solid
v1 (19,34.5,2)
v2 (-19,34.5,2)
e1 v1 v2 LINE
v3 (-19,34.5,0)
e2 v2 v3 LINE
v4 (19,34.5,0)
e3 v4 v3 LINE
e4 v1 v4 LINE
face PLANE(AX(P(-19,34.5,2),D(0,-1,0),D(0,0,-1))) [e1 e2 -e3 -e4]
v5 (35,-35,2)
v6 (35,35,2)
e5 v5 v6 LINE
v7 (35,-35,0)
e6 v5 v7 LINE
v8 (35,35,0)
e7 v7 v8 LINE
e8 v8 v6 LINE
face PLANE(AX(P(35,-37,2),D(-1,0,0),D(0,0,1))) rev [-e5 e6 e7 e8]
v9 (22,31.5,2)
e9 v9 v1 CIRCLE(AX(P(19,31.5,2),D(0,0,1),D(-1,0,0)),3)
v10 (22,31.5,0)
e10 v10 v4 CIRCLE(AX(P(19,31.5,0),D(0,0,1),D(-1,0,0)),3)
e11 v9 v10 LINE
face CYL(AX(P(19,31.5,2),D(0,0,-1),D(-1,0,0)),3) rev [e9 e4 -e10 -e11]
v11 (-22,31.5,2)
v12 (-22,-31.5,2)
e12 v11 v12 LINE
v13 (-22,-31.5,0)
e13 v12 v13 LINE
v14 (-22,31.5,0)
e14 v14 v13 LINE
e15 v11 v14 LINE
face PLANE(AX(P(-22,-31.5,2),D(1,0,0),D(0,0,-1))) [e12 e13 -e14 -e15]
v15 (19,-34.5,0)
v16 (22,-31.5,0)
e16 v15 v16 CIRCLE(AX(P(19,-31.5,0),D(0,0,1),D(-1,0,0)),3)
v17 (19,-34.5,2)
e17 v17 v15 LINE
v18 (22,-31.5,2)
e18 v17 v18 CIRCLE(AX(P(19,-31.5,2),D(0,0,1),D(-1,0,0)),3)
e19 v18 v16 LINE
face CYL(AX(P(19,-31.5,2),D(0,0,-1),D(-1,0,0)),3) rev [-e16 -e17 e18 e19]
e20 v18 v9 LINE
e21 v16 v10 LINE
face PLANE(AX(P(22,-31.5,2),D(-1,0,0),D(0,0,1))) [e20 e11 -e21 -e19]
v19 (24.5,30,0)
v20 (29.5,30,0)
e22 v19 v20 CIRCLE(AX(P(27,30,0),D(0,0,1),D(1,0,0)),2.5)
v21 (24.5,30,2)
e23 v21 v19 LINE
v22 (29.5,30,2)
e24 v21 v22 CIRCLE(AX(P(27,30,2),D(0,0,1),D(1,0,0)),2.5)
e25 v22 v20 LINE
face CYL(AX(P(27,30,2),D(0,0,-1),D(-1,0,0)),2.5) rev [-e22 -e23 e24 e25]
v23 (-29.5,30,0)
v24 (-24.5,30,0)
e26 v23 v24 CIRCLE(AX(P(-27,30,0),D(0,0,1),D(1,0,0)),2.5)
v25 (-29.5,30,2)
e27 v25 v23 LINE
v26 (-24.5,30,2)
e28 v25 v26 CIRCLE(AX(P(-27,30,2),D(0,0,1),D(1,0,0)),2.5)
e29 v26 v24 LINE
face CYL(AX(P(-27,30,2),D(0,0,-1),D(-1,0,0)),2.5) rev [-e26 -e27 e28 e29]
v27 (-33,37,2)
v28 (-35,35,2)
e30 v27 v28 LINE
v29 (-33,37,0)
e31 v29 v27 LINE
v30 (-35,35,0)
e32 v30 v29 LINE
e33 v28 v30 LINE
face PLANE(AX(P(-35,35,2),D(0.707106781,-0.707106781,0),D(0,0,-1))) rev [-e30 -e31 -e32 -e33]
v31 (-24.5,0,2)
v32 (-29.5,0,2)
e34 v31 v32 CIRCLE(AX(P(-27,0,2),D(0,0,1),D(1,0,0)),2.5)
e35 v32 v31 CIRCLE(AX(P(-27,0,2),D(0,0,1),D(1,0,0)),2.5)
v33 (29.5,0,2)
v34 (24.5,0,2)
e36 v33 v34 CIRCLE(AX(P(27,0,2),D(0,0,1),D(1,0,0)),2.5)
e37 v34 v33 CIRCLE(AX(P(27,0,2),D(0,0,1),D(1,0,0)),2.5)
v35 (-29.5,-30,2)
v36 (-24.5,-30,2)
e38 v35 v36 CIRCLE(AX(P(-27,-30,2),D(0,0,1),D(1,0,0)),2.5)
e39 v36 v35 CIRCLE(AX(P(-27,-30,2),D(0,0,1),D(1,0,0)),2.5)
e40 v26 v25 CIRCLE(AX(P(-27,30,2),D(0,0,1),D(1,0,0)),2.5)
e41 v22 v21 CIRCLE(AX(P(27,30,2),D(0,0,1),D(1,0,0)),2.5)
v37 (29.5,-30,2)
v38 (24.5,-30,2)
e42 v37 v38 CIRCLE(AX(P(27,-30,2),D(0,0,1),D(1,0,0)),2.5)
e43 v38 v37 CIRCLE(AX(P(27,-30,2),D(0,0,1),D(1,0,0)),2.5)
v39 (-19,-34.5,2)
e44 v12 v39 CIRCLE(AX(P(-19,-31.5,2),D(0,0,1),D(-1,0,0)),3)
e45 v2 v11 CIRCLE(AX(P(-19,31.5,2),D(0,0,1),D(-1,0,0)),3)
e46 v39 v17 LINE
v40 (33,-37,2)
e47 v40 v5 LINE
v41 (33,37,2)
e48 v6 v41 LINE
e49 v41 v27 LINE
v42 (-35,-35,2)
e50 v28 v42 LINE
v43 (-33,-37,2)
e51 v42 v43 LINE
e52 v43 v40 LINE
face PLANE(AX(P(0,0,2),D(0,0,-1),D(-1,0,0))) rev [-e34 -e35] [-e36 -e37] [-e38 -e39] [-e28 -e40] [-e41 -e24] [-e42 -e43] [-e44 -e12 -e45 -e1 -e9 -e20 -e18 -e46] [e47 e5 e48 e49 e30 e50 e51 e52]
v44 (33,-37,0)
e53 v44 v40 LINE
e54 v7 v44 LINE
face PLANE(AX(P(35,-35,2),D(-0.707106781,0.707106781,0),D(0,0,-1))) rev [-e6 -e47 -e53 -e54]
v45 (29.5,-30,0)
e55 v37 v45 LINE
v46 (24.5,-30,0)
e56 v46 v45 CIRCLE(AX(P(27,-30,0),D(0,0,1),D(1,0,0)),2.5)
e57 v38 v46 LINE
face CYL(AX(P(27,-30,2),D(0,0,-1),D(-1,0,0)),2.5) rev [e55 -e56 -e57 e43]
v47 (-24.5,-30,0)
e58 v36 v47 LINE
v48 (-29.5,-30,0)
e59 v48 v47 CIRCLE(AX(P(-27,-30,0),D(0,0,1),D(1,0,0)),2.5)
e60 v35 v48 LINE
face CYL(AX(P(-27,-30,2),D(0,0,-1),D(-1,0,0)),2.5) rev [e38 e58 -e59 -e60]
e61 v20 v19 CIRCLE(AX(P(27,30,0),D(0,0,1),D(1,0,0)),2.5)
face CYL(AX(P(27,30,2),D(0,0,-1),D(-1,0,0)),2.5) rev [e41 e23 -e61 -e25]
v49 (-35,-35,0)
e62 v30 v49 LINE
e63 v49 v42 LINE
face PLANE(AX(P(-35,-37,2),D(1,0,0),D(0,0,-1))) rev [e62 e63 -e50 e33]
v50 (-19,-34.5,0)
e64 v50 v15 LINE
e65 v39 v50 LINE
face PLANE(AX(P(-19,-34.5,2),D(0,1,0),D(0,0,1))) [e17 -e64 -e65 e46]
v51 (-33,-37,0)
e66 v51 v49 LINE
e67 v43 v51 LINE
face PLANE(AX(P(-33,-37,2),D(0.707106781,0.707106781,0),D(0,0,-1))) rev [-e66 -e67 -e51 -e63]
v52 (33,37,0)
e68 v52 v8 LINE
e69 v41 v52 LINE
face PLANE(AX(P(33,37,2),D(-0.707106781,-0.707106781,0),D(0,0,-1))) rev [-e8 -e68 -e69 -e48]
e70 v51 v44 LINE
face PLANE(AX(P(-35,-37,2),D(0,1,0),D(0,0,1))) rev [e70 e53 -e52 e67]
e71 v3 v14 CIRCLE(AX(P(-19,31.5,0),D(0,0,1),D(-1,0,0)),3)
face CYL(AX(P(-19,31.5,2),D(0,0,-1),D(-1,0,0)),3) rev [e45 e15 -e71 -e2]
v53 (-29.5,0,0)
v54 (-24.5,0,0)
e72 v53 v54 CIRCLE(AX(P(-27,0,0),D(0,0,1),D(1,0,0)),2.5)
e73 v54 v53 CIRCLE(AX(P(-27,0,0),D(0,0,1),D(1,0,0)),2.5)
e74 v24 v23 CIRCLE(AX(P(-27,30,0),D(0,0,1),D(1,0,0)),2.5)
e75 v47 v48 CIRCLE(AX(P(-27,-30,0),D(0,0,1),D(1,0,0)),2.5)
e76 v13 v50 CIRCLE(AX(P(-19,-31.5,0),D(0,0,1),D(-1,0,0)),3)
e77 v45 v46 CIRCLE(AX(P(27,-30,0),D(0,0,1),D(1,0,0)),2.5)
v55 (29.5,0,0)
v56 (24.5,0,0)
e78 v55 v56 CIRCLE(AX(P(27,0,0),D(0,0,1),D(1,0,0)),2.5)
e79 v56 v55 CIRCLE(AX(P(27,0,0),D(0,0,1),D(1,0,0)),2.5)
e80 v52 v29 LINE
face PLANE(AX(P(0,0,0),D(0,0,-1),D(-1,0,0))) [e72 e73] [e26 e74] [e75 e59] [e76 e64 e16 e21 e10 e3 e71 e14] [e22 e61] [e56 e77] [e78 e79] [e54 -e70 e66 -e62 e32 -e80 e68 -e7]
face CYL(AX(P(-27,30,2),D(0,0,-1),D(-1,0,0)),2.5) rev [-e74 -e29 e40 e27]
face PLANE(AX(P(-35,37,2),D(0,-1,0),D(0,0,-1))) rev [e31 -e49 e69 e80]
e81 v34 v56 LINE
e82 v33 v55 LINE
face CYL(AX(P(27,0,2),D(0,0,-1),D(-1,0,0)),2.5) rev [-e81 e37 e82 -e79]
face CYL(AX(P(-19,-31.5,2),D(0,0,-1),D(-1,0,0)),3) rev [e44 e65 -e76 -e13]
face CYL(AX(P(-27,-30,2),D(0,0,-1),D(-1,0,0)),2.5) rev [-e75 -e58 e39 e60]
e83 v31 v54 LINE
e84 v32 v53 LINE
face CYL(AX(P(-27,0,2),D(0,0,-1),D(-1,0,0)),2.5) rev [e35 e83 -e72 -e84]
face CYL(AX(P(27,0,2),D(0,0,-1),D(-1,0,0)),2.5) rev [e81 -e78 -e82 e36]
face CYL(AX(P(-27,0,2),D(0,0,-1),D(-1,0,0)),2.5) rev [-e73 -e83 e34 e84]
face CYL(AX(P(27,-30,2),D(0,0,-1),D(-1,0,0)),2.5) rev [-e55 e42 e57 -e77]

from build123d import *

# Parameters (mm, degrees)
SKETCH1_W           = 70
SKETCH1_H           = 74
SKETCH1_R           = 2.5
BOSS_EXTRUDE1_DEPTH = 2
CHAMFER1_SIZE       = 2


with BuildPart() as part:
    # Sketch1 → Boss-Extrude1 (new body)
    with BuildSketch(Plane.XY):
        Rectangle(SKETCH1_W, SKETCH1_H)
        with Locations((-27, 30)):
            Circle(SKETCH1_R, mode=Mode.SUBTRACT)
        with Locations((-27, 0)):
            Circle(SKETCH1_R, mode=Mode.SUBTRACT)
        with Locations((-27, -30)):
            Circle(SKETCH1_R, mode=Mode.SUBTRACT)
        with Locations((27, -30)):
            Circle(SKETCH1_R, mode=Mode.SUBTRACT)
        with Locations((27, 0)):
            Circle(SKETCH1_R, mode=Mode.SUBTRACT)
        with Locations((27, 30)):
            Circle(SKETCH1_R, mode=Mode.SUBTRACT)
        with BuildLine():
            Line((-19, -34.5), (19, -34.5))
            ThreePointArc((19, -34.5), (21.121320344, -33.621320344), (22, -31.5))
            Line((22, -31.5), (22, 31.5))
            ThreePointArc((22, 31.5), (21.121320344, 33.621320344), (19, 34.5))
            Line((19, 34.5), (-19, 34.5))
            ThreePointArc((-19, 34.5), (-21.121320344, 33.621320344), (-22, 31.5))
            Line((-22, 31.5), (-22, -31.5))
            ThreePointArc((-22, -31.5), (-21.121320344, -33.621320344), (-19, -34.5))
        make_face(mode=Mode.SUBTRACT)
    extrude(amount=BOSS_EXTRUDE1_DEPTH)

    # Chamfer1
    chamfer1_edges = [part.edges().sort_by_distance(p)[0] for p in [
        (35, -37, 1),
        (-35, -37, 1),
        (-35, 37, 1),
        (35, 37, 1),
    ]]
    chamfer(chamfer1_edges, length=CHAMFER1_SIZE)


solid = part.part
